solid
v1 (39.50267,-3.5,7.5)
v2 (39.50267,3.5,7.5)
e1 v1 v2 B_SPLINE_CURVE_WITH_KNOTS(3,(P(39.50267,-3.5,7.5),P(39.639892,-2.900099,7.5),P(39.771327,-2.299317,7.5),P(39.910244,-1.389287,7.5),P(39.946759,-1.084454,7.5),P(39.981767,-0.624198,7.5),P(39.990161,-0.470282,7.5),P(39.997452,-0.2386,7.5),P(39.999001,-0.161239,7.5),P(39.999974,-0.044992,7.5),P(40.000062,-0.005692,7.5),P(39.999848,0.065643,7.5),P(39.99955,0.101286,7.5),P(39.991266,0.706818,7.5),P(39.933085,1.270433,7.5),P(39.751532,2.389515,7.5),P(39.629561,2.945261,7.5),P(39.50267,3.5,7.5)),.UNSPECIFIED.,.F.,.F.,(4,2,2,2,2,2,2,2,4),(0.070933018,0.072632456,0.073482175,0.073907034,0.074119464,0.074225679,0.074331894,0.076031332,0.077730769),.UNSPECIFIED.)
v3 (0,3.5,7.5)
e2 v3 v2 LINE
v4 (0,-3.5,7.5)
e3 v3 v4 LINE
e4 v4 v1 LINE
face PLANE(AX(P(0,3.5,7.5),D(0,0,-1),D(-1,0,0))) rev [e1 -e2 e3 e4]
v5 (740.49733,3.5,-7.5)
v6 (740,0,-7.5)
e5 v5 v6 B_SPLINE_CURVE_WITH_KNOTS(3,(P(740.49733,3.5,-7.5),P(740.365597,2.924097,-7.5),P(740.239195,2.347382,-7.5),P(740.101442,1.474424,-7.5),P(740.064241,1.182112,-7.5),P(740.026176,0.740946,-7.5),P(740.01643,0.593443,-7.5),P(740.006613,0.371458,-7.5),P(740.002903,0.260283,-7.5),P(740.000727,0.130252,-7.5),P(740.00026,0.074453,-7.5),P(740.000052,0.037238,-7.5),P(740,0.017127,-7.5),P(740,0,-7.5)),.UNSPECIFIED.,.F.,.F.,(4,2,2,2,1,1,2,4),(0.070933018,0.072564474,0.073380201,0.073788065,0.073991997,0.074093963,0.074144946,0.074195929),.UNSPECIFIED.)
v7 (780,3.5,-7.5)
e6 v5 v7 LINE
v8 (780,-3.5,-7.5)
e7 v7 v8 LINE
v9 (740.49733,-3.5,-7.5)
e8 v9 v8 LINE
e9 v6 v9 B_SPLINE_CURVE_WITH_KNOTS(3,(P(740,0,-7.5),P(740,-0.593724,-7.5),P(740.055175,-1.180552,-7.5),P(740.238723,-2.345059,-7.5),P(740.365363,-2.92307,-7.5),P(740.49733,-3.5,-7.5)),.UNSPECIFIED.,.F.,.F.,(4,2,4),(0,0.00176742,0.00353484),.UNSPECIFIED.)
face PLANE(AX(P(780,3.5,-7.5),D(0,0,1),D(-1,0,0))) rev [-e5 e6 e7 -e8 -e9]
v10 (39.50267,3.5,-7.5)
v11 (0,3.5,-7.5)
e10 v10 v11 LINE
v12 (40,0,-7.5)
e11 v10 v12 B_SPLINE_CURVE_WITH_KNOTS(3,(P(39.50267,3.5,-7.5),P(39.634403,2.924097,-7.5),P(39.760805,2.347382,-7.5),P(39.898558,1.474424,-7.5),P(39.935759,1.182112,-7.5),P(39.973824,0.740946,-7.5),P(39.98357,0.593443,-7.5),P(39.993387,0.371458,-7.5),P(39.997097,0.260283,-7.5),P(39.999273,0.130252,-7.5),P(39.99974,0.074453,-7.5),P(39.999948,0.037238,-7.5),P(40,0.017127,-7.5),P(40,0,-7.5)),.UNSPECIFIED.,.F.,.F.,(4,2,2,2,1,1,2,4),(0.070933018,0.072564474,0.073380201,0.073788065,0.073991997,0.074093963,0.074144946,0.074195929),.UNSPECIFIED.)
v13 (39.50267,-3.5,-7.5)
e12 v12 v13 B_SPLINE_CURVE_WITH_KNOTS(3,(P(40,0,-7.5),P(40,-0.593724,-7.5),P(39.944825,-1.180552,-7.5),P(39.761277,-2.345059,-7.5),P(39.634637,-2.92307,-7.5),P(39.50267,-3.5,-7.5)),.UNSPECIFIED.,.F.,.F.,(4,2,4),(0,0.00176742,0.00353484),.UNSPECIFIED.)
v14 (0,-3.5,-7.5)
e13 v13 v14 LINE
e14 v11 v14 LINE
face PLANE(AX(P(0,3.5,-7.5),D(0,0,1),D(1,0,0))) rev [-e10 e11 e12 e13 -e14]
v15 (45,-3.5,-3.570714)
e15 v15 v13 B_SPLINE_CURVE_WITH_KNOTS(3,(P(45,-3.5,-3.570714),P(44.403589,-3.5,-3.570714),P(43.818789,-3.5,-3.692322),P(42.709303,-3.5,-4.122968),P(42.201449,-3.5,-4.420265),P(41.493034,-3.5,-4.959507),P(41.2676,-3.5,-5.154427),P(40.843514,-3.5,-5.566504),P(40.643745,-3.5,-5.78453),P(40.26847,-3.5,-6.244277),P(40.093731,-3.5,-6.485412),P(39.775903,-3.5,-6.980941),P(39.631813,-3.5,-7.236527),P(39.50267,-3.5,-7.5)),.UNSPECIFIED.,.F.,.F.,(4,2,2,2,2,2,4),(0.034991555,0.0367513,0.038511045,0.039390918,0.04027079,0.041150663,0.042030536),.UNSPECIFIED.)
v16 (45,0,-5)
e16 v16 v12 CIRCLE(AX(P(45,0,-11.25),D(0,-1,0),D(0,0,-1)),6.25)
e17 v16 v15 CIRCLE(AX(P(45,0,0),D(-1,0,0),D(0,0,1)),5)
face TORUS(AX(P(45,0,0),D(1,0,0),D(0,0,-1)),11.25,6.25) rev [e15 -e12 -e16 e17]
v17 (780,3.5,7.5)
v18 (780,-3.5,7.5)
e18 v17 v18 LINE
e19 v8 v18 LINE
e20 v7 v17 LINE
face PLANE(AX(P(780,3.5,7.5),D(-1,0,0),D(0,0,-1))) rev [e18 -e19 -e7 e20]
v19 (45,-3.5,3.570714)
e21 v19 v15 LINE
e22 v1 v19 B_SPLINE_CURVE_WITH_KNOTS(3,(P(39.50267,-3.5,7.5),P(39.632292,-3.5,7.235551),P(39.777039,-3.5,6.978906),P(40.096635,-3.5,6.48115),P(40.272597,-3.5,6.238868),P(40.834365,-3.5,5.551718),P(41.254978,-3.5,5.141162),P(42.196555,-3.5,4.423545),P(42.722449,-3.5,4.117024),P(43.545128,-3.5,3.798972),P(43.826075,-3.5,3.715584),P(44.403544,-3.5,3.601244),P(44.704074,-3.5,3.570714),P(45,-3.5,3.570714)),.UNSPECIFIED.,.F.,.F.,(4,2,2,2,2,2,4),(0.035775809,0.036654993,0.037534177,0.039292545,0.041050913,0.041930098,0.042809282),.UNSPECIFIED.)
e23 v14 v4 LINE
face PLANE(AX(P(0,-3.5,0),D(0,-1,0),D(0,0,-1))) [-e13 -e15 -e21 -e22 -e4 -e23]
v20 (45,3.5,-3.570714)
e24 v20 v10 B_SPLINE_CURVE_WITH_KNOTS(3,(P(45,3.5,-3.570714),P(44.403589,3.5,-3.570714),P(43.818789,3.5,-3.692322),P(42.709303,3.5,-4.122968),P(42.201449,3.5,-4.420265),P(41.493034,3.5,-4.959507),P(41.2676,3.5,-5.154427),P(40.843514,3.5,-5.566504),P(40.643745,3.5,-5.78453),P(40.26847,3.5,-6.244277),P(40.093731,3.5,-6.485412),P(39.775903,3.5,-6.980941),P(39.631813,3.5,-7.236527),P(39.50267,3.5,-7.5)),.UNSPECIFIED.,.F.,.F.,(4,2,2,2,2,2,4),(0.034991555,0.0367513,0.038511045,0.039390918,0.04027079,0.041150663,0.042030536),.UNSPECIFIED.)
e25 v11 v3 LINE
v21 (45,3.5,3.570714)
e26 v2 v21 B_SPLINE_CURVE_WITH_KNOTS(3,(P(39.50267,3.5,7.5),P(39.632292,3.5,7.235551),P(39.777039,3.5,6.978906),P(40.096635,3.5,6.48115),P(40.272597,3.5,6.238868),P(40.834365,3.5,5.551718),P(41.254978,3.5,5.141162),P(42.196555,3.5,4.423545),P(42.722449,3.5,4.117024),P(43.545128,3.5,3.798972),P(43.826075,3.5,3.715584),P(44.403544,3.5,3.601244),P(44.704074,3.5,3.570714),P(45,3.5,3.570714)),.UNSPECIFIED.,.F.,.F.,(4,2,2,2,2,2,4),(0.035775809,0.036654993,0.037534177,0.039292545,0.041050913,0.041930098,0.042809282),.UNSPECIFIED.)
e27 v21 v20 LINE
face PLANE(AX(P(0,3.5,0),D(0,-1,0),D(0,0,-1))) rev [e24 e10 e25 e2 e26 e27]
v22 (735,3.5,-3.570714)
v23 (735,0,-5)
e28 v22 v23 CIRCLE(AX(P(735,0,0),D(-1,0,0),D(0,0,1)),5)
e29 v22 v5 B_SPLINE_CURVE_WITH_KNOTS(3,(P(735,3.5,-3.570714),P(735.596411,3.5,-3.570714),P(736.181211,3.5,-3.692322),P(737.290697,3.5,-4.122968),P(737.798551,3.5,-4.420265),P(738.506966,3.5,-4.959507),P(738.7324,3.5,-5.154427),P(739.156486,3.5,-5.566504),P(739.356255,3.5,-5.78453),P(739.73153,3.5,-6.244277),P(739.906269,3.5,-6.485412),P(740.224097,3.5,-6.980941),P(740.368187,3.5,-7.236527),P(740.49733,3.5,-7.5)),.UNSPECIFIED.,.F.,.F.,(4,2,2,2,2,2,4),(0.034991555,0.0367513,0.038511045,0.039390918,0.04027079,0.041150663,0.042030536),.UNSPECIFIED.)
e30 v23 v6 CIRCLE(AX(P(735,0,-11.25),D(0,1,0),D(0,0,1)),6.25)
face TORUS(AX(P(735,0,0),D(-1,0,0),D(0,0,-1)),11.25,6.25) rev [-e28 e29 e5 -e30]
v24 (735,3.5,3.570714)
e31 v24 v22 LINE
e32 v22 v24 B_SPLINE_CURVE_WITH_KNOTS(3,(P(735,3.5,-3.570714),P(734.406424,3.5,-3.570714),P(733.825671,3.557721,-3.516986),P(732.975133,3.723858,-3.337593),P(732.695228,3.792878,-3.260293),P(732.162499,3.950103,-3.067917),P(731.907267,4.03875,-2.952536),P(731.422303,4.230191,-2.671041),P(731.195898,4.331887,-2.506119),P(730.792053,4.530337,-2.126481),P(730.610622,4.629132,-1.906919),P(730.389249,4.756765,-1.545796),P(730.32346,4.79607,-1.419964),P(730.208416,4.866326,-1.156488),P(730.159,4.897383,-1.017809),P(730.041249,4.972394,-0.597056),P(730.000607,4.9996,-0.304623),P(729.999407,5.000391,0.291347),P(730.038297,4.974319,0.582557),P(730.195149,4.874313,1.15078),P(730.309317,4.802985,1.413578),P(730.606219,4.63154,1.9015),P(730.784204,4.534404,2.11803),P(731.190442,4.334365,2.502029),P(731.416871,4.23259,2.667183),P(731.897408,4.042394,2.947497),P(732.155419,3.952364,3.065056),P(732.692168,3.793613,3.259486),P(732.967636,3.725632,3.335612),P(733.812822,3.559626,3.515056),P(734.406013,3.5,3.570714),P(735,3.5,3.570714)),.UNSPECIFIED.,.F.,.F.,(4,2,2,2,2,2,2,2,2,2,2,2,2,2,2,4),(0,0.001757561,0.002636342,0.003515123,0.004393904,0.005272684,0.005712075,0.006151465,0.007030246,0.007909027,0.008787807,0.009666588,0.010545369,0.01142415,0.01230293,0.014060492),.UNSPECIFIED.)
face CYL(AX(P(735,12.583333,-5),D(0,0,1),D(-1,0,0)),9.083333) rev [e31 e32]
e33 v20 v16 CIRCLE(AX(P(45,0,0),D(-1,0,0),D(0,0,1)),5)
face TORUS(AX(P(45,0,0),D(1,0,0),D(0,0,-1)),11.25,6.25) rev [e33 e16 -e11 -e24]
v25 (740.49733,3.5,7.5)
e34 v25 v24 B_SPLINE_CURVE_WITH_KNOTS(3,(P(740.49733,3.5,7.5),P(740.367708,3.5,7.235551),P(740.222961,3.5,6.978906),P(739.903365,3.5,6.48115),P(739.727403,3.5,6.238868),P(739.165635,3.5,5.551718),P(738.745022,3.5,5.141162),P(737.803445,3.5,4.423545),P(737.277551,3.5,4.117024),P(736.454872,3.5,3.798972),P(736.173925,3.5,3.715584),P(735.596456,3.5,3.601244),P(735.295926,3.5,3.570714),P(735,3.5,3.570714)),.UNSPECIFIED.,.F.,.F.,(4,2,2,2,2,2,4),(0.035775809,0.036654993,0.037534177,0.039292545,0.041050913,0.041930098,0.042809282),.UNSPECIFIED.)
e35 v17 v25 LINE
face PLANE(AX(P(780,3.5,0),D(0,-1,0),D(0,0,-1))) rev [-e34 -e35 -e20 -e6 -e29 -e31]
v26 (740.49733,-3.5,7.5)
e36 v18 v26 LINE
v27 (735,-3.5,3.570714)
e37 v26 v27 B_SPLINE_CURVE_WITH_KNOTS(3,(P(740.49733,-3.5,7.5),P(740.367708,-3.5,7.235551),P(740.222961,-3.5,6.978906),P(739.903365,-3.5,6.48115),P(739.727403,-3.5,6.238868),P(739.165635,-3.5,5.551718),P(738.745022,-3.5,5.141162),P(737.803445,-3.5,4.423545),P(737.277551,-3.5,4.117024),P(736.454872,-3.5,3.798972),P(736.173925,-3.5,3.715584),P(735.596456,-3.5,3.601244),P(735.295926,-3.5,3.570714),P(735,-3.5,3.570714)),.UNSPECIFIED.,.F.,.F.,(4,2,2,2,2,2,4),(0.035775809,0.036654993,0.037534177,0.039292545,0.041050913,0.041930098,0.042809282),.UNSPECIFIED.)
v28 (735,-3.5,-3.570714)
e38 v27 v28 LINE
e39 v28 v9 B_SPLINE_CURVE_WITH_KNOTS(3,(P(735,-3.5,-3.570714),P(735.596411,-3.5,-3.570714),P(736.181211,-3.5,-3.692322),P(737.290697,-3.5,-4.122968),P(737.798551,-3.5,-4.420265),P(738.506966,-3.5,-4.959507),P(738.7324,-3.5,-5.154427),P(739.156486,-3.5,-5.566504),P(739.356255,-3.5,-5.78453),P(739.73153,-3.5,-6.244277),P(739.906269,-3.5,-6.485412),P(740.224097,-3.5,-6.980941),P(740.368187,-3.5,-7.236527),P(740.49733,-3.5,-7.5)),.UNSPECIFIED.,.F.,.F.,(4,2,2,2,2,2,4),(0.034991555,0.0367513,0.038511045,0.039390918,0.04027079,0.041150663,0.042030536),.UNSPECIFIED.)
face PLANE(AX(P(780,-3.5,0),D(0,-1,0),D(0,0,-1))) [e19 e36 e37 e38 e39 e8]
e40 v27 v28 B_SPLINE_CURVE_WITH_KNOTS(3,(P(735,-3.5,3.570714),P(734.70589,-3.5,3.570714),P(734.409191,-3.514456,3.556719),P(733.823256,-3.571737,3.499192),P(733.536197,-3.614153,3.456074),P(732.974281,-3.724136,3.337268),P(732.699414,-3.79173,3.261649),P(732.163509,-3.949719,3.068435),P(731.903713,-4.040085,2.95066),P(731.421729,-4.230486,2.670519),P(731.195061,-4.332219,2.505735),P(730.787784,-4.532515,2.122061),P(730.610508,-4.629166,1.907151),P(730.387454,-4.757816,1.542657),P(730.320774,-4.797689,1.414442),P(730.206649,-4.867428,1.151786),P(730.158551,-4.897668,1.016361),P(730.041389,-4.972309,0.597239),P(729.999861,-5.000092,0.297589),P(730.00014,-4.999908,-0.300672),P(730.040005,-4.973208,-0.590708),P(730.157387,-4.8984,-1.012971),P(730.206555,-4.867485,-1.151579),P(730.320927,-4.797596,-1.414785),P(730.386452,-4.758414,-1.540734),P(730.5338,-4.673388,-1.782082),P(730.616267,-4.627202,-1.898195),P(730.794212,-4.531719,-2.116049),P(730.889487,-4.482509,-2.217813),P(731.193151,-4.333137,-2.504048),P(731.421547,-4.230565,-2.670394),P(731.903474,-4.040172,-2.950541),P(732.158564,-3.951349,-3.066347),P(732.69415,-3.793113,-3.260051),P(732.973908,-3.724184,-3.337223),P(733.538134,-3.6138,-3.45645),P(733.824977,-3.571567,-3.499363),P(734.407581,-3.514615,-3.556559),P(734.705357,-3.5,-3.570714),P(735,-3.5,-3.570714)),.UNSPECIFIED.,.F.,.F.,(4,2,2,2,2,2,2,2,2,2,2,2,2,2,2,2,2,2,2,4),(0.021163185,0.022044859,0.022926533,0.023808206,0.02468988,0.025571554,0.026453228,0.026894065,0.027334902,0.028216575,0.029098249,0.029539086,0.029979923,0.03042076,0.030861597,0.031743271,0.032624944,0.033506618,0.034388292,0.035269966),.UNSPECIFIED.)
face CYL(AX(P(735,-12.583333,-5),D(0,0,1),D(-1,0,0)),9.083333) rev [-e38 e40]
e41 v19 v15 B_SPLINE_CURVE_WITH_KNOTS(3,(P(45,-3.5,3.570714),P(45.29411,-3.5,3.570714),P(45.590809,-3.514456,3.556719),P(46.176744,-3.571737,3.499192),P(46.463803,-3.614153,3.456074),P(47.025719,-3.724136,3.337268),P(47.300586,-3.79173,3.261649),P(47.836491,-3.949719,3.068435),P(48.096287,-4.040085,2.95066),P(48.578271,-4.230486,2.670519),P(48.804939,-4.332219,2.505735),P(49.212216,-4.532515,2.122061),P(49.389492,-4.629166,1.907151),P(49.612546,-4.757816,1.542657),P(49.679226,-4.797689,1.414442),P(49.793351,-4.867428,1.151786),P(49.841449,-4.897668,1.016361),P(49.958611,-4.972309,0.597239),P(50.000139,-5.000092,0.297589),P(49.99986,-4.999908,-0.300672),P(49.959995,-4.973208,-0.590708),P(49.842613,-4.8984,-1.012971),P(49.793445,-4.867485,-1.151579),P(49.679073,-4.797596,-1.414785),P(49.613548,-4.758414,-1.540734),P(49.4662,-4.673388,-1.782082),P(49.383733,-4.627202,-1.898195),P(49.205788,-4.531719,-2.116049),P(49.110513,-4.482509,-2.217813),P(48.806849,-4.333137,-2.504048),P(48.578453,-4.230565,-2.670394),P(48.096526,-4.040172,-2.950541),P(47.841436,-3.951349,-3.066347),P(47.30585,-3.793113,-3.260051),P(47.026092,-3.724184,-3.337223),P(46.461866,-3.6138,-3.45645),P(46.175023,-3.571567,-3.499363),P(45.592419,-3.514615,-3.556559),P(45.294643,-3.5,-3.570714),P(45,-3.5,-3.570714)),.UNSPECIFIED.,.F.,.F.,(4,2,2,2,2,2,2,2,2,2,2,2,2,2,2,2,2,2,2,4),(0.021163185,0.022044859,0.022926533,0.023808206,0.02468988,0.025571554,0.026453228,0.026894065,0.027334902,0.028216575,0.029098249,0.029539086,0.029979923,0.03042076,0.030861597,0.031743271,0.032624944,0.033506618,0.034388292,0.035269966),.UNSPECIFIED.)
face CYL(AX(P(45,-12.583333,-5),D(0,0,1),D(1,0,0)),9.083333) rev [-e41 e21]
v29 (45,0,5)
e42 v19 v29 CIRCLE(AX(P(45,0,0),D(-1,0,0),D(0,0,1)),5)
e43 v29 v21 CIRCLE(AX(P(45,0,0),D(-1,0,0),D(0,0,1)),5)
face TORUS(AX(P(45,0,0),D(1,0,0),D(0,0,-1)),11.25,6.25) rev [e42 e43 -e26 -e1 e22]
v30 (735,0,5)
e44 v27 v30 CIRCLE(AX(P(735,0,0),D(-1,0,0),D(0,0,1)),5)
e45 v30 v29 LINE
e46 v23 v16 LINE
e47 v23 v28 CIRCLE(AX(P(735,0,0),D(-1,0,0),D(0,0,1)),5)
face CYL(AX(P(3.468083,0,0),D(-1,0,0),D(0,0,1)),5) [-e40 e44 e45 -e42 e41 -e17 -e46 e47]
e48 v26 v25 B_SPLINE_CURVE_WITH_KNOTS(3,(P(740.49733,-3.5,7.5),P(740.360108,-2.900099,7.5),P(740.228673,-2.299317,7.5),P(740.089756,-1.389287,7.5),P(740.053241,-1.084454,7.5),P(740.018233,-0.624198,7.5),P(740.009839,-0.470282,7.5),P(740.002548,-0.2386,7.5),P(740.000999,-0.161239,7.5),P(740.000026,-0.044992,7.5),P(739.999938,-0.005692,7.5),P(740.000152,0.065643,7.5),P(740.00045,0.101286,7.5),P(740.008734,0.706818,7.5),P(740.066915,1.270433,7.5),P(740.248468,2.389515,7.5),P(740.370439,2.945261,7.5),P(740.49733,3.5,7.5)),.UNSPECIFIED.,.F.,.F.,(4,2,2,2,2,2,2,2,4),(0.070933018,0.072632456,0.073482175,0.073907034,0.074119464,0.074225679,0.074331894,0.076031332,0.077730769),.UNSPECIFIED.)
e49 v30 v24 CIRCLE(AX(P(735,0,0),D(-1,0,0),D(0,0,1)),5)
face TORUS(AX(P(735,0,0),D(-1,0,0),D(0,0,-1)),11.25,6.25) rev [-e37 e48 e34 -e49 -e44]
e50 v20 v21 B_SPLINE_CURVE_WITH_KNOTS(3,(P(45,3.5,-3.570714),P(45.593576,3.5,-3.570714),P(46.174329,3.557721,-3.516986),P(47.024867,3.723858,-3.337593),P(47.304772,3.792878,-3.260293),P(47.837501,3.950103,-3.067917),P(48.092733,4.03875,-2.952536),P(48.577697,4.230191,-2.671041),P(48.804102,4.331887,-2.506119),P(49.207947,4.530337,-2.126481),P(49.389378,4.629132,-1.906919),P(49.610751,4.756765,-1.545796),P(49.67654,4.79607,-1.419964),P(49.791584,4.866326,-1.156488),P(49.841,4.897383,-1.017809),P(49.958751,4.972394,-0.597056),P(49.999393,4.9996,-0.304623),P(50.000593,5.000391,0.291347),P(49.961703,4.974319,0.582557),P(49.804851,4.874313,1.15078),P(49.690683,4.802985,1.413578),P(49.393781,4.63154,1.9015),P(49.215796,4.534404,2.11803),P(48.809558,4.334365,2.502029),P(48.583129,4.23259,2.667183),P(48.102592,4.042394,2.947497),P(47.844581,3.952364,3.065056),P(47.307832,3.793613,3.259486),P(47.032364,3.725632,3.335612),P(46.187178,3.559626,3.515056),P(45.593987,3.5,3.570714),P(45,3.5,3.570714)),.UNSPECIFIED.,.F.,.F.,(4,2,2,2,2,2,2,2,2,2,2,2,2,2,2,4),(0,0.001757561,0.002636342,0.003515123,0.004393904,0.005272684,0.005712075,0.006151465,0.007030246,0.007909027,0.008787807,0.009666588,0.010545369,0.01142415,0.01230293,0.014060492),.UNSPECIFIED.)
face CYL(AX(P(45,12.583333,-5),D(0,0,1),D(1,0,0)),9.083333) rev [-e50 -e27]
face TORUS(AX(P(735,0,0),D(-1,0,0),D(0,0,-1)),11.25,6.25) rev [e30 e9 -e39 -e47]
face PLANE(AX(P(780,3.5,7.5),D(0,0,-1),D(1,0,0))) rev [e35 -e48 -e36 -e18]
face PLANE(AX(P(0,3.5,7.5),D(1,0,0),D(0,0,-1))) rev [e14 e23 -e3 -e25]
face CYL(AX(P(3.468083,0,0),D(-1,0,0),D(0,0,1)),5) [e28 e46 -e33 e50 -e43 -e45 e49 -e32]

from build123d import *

# Parameters (mm, degrees)
SKETCH_1_W          = 45
SKETCH_1_H          = 15
EXTRUDE_1_DEPTH     = 3.5
CUT_EXTRUDE_1_DEPTH = 5
SKETCH_5_R          = 5
EXTRUDE_2_DEPTH     = 290


with BuildPart() as part:
    # 草图1 → 凸台-拉伸1 (new, symmetric)
    with BuildSketch(Plane(origin=(0, 0, 0), x_dir=(1, 0, 0), z_dir=(0, 1, 0))):
        with Locations((22.5, 0)):
            Rectangle(SKETCH_1_W, SKETCH_1_H)
    extrude(amount=EXTRUDE_1_DEPTH, both=True)

    # 草图2 → 旋转1 (revolve)
    with BuildSketch(Plane.XY, mode=Mode.PRIVATE) as revolve_1_sk:
        Polygon((45, 3.5), (45, 0), (100, 0), (100, 5), (50, 5), (45, 5), align=None)
    revolve(revolve_1_sk.sketch.rotate(Axis((3.468083249, 0, 0), (1, 0, 0)), 90), axis=Axis((3.468083249, 0, 0), (1, 0, 0)))

    # 草图3 → 切除-拉伸1 (cut, symmetric)
    with BuildSketch(Plane.XY):
        with BuildLine():
            Line((50, -5), (50, -7.872092098))
            Line((50, -7.872092098), (45, -7.872092098))
            Line((45, -7.872092098), (45, -3.5))
            ThreePointArc((45, -3.5), (47.610076627, -3.883077909), (50, -5))
        make_face()
        with BuildLine():
            Line((45, 3.5), (45, 6.877663773))
            Line((45, 6.877663773), (50, 6.877663773))
            Line((50, 6.877663773), (50, 5))
            ThreePointArc((50, 5), (47.610076627, 3.883077909), (45, 3.5))
        make_face()
    extrude(amount=CUT_EXTRUDE_1_DEPTH, both=True, mode=Mode.SUBTRACT)

    # 草图4 → 切除-旋转1 (revolve, cut)
    with BuildSketch(Plane(origin=(0, 0, 0), x_dir=(1, 0, 0), z_dir=(0, 1, 0))):
        with BuildLine():
            Line((40, 11.25), (45, 11.25))
            Line((45, 11.25), (45, 5))
            ThreePointArc((45, 5), (42.204915028, 5.659830056), (40, 7.5))
            ThreePointArc((40, 7.5), (39.341282089, 8.596434171), (38.919571519, 9.804009168))
            Line((38.919571519, 9.804009168), (40, 11.25))
        make_face()
    revolve(axis=Axis((45, 0, 0), (-1, 0, 0)), mode=Mode.SUBTRACT)

    # 草图5 → 凸台-拉伸2 (add)
    with BuildSketch(Plane(origin=(100, 0, 0), x_dir=(0, 0, -1), z_dir=(1, 0, 0))):
        with Locations(Location((0, 0, 0), (0, 0, 135.572995999))):
            Circle(SKETCH_5_R)
    extrude(amount=EXTRUDE_2_DEPTH)

    # 镜向1: part across plane


with BuildPart() as part_1:
    add(part.part)
    add(part.part.mirror(Plane(origin=(390, 0, 0), x_dir=(0, 0, 1), z_dir=(1, 0, 0))))


solid = part_1.part
